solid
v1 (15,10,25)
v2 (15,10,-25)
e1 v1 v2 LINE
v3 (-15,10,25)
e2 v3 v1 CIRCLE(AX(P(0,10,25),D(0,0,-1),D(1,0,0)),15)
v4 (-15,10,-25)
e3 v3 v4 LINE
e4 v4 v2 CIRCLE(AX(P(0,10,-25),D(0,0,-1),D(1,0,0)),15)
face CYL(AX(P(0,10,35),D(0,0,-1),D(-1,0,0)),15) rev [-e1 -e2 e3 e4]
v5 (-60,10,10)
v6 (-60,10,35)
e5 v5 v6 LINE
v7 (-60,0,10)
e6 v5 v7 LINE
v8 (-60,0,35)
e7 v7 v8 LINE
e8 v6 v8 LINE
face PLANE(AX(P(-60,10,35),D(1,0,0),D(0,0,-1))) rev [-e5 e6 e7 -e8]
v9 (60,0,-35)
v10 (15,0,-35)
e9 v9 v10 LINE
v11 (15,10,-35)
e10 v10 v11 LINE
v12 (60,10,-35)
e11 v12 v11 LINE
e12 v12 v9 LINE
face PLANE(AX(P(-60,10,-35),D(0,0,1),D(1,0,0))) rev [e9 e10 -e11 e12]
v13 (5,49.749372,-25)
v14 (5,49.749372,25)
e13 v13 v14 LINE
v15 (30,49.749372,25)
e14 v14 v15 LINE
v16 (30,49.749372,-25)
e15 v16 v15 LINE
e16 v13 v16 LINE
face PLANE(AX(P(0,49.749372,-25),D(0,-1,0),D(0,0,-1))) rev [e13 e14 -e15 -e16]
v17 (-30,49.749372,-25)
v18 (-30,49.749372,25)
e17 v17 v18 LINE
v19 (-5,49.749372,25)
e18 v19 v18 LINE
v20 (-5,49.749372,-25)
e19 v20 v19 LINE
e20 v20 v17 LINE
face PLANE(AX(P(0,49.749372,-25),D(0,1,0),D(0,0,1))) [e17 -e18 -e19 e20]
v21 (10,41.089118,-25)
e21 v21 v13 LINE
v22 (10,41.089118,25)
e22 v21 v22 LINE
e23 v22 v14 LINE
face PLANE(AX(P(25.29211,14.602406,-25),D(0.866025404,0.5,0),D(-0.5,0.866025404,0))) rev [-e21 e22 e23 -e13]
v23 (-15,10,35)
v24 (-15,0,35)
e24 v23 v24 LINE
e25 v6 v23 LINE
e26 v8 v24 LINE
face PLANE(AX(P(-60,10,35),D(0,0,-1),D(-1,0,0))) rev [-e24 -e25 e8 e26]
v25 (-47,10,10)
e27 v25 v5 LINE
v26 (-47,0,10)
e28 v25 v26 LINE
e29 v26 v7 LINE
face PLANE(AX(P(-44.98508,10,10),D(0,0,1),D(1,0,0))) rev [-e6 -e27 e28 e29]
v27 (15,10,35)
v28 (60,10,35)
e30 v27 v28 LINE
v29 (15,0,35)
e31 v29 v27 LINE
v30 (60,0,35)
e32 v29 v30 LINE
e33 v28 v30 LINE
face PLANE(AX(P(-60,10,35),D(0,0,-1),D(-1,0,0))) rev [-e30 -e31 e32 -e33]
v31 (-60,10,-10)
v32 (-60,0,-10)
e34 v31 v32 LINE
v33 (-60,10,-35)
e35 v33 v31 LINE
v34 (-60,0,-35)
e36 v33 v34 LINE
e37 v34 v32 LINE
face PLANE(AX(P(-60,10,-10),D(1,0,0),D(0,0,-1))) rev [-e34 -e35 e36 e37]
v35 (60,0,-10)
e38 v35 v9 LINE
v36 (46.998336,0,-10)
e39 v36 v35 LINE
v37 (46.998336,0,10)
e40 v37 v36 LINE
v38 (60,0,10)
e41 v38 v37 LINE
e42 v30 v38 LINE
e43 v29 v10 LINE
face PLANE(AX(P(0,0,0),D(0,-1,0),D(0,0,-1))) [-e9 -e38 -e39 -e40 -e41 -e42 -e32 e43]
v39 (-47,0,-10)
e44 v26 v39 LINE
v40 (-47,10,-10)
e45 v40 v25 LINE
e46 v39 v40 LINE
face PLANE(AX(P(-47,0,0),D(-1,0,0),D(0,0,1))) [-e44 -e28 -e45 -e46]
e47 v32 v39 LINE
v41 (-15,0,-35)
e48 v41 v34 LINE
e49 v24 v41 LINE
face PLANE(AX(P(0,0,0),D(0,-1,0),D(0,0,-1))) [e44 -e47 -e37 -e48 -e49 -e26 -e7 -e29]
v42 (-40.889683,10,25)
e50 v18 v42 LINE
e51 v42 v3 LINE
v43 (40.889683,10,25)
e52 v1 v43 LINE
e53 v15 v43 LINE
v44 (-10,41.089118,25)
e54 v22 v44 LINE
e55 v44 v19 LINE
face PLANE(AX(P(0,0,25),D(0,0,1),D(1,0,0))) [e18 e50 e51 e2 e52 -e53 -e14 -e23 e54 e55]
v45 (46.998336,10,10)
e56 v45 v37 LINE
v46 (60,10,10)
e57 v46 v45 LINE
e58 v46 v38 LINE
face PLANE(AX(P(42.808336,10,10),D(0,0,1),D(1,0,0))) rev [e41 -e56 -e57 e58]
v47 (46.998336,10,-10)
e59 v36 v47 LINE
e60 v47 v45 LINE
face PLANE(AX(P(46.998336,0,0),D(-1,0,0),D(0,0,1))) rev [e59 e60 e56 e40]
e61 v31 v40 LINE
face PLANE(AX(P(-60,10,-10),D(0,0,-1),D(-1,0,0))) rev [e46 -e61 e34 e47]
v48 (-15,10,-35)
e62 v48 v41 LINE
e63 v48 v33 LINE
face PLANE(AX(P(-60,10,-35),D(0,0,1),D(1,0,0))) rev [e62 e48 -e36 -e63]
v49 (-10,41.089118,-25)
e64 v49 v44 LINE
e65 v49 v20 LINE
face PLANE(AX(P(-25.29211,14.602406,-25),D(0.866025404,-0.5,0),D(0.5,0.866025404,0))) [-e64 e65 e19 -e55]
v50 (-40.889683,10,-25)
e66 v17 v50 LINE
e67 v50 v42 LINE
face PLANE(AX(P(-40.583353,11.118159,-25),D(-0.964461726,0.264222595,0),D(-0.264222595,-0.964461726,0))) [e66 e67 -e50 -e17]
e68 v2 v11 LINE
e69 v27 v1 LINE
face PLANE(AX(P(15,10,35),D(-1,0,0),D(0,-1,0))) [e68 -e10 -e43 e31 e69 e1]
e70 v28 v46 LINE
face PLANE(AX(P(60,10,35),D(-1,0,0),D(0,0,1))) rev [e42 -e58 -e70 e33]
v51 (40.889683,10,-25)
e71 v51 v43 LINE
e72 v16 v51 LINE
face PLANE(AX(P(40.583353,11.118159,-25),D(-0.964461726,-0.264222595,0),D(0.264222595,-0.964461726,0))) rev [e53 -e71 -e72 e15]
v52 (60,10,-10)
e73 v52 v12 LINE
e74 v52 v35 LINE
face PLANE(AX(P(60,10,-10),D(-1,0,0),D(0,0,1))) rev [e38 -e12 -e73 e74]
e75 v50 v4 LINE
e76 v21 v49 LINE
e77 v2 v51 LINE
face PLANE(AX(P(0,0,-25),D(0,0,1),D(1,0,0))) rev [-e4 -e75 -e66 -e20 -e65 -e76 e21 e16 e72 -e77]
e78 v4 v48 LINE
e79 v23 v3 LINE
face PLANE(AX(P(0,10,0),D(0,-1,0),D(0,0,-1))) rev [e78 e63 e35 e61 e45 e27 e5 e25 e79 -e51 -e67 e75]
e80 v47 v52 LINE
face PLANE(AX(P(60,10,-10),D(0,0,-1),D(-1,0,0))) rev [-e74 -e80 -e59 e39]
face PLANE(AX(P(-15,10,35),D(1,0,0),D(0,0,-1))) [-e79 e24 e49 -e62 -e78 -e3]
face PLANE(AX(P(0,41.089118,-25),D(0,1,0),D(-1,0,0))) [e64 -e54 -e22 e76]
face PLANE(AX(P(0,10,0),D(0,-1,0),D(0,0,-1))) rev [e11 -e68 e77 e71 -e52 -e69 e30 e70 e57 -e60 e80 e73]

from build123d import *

# Parameters (mm, degrees)
BASE_PLATE_10MM_DEPTH         = 10
SUPPORT_BLOCK_50MM_DEPTH      = 25
SUPPORT_BLOCK_50MM_DEPTH_BACK = 25
ARCH_THROUGH_CUT_DEPTH        = 35
ARCH_THROUGH_CUT_DEPTH_BACK   = 35
UPPER_BOSS_SKETCH_W           = 20
UPPER_BOSS_SKETCH_H           = 10
UPPER_BOSS_3MM_DEPTH          = 3
BASE_PAD_SKETCH_W             = 20
BASE_PAD_SKETCH_H             = 10
BASE_PAD_4_19MM_DEPTH         = 4.19


with BuildPart() as part:
    # Base Plate Sketch → Base Plate 10mm (new body)
    with BuildSketch(Plane(origin=(0, 0, 0), x_dir=(1, 0, 0), z_dir=(0, 1, 0))):
        Polygon((60, 10), (42.8083356, 10), (42.8083356, -10), (60, -10), (60, -35), (-60, -35), (-60, -10), (-44.9850804, -10), (-44.9850804, 10), (-60, 10), (-60, 35), (60, 35), align=None)
    extrude(amount=BASE_PLATE_10MM_DEPTH)

    # Support Block Profile → Support Block 50mm (add, two sides: drawn at the far end of the back side and taken through both)
    with BuildSketch(Plane.XY.offset(-SUPPORT_BLOCK_50MM_DEPTH_BACK)):
        with BuildLine():
            Line((-40.889682702, 10), (-15, 10))
            ThreePointArc((-15, 10), (0, 25), (15, 10))
            Line((15, 10), (40.889682702, 10))
            Line((40.889682702, 10), (30, 49.749371855))
            Line((30, 49.749371855), (5, 49.749371855))
            Line((5, 49.749371855), (10, 41.089117817))
            Line((10, 41.089117817), (-10, 41.089117817))
            Line((-10, 41.089117817), (-5, 49.749371855))
            Line((-5, 49.749371855), (-30, 49.749371855))
            Line((-30, 49.749371855), (-40.889682702, 10))
        make_face()
        with BuildLine():
            ThreePointArc((15, 10), (0, 25), (-15, 10))
            Line((-15, 10), (0, 10))
            Line((0, 10), (15, 10))
        make_face()
    extrude(amount=SUPPORT_BLOCK_50MM_DEPTH + SUPPORT_BLOCK_50MM_DEPTH_BACK)

    # Arch Cut Sketch → Arch Through Cut (cut, two sides: drawn at the far end of the back side and taken through both)
    with BuildSketch(Plane.XY.offset(-ARCH_THROUGH_CUT_DEPTH_BACK)):
        with BuildLine():
            Line((-15, 10), (-15, 0))
            Line((-15, 0), (15, 0))
            Line((15, 0), (15, 10))
            ThreePointArc((15, 10), (0, 25), (-15, 10))
        make_face()
    extrude(amount=ARCH_THROUGH_CUT_DEPTH + ARCH_THROUGH_CUT_DEPTH_BACK, mode=Mode.SUBTRACT)

    # Upper Boss Sketch → Upper Boss 3mm (add)
    with BuildSketch(Plane(origin=(-44, 0, 0), x_dir=(0, 0, -1), z_dir=(1, 0, 0))):
        with Locations((0, 5)):
            Rectangle(UPPER_BOSS_SKETCH_W, UPPER_BOSS_SKETCH_H)
    extrude(amount=-UPPER_BOSS_3MM_DEPTH)

    # Base Pad Sketch → Base Pad 4.19mm (add)
    with BuildSketch(Plane(origin=(42.8083356, 0, 0), x_dir=(0, 0, -1), z_dir=(1, 0, 0))):
        with Locations((0, 5)):
            Rectangle(BASE_PAD_SKETCH_W, BASE_PAD_SKETCH_H)
    extrude(amount=BASE_PAD_4_19MM_DEPTH)


solid = part.part
